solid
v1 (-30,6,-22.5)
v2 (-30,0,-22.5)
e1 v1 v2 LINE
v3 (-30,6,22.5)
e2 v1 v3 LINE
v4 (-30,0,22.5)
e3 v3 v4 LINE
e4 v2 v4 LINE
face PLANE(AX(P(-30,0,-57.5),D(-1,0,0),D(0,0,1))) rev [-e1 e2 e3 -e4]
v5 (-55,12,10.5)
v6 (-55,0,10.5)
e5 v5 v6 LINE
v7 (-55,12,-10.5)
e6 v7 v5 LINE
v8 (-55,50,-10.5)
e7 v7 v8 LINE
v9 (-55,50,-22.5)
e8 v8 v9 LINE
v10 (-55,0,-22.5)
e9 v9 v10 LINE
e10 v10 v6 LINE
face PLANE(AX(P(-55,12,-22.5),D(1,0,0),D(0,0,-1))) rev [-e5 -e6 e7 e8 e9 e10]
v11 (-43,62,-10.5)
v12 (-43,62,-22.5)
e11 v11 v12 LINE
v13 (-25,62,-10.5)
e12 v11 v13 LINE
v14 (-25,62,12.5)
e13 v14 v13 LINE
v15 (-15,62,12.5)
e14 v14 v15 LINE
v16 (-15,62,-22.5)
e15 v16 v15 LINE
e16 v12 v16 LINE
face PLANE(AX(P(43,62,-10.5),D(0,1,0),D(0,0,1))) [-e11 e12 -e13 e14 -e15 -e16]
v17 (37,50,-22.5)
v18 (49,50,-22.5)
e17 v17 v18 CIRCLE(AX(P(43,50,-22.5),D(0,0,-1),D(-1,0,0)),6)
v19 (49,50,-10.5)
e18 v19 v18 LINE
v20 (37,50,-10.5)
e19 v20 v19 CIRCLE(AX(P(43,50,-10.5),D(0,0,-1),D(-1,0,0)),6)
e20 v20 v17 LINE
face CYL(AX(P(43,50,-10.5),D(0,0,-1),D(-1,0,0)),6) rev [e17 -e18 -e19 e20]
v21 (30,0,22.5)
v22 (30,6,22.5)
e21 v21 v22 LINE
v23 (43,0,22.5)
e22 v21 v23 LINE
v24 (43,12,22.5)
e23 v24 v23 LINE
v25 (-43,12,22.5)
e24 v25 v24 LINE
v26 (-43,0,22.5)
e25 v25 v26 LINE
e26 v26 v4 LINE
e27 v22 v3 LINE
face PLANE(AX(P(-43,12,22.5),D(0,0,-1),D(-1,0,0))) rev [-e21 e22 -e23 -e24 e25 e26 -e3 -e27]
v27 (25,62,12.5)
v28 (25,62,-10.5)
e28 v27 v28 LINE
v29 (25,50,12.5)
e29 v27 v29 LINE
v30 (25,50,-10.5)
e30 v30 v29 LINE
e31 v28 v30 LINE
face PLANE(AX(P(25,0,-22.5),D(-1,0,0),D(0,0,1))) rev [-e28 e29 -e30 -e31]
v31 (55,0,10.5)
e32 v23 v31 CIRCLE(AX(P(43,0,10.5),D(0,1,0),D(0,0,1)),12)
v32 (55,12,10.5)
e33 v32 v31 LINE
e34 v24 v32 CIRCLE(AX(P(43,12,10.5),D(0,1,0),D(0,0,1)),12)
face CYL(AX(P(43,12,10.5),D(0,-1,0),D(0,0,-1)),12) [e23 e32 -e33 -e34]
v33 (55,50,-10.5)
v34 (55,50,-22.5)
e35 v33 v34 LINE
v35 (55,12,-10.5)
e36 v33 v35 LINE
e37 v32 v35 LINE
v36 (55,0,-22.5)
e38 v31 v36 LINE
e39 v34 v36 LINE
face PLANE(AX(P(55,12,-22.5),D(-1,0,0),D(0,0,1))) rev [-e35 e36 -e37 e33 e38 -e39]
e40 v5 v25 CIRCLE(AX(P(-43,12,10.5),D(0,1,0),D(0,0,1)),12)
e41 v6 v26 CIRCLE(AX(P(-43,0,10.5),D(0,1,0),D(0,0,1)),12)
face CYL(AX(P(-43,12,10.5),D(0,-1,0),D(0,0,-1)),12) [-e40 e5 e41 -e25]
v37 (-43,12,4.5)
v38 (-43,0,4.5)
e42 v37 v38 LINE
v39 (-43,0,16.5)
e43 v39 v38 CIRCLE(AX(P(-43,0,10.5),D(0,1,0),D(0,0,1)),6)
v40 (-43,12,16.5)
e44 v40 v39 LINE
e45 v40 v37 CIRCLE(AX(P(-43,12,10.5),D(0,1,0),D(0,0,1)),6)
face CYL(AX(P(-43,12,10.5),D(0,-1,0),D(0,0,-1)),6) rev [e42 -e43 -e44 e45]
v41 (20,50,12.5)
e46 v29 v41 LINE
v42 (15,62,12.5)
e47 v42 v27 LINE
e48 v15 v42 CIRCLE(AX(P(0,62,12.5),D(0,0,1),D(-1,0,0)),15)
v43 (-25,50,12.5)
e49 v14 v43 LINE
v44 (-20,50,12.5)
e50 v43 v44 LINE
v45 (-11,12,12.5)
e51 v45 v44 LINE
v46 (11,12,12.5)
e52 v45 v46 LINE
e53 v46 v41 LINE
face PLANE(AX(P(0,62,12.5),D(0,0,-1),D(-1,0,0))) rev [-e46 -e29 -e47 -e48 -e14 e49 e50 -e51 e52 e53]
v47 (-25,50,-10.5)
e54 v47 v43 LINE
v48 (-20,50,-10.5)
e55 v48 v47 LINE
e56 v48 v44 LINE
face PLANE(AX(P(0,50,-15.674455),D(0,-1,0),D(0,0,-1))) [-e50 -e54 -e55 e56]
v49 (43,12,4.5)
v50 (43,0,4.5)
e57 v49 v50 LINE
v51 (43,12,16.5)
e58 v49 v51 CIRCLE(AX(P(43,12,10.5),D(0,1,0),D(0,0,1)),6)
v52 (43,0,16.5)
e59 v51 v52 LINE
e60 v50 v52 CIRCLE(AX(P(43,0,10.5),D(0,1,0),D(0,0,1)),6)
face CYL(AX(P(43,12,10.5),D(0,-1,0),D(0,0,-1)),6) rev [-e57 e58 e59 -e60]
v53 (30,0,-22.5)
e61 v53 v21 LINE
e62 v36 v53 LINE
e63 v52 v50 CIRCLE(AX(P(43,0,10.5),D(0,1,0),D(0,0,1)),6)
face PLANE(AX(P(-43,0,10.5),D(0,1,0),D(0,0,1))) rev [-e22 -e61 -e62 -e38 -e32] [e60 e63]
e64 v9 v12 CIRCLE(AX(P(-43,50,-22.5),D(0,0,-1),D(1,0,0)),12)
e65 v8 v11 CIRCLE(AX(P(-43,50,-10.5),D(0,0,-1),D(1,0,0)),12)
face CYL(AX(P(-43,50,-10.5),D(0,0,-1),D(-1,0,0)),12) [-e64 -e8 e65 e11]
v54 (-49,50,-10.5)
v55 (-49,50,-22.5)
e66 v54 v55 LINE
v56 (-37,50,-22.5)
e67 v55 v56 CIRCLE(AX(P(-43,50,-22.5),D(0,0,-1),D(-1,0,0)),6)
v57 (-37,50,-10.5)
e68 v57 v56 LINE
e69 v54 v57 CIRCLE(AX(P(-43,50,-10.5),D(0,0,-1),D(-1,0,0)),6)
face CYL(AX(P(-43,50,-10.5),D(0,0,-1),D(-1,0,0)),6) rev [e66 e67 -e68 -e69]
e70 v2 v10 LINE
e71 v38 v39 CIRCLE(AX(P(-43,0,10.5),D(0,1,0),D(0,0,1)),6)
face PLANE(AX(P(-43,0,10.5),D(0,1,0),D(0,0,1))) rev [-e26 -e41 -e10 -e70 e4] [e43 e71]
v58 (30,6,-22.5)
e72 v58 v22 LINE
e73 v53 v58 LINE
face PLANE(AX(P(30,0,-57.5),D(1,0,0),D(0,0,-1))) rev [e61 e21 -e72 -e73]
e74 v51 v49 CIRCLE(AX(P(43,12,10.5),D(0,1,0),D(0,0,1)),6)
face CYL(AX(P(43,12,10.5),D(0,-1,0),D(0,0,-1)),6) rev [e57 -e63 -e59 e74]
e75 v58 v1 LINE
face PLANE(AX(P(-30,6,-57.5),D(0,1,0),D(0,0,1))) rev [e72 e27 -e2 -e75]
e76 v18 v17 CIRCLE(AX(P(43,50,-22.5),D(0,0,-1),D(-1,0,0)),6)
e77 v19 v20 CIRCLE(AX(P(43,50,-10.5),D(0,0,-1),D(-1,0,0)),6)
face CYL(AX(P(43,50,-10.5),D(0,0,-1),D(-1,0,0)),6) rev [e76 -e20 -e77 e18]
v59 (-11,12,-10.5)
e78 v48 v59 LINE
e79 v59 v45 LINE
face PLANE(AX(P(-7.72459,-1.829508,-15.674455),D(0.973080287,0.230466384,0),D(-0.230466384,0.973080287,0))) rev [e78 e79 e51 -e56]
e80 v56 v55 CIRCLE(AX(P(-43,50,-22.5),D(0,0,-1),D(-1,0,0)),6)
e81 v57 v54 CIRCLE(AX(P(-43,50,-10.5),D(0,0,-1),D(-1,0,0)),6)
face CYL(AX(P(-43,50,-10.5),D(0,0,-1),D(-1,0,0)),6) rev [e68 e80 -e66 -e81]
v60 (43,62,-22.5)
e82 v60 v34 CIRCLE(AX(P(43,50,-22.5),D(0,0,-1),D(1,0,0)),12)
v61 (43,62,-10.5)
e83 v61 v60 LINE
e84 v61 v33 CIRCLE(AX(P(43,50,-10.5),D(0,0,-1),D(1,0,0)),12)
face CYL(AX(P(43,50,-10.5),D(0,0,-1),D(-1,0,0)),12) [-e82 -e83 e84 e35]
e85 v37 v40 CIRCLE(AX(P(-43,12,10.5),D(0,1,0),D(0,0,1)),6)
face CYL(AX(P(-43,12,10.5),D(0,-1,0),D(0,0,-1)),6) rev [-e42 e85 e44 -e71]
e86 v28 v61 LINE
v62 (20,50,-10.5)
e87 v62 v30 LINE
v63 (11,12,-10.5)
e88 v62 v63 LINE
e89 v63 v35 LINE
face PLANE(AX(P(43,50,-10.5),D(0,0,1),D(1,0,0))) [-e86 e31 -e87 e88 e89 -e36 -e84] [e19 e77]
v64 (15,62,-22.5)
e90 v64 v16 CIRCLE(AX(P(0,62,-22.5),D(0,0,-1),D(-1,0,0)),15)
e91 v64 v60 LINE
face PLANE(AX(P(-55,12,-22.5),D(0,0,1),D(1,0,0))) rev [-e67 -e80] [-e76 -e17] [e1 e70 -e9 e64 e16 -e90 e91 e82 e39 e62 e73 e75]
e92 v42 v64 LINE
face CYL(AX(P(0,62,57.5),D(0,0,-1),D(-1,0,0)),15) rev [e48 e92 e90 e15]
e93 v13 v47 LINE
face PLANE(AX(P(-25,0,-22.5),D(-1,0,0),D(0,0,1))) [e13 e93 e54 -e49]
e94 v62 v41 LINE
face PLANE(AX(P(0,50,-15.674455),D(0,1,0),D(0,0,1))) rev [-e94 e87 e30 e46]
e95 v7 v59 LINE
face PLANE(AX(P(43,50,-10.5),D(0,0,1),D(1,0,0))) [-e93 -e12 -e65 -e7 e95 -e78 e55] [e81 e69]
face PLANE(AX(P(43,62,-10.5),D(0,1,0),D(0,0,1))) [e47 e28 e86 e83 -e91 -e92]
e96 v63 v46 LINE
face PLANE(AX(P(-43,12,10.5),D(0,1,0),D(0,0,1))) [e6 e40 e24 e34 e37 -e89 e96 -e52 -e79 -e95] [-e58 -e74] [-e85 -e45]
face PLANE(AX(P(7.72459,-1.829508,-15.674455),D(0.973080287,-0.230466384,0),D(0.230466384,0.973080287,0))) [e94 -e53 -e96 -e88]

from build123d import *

# Parameters (mm, degrees)
BASE_PLATE_SKETCH_R            = 6
BASE_PLATE_110X45X12_DEPTH     = 12
BACK_WALL_SKETCH_R             = 6
BACK_WALL_12MM_DEPTH           = 12
BASE_UNDERSIDE_SLOT_SKETCH_W   = 60
BASE_UNDERSIDE_SLOT_SKETCH_H   = 6
BASE_UNDERSIDE_SLOT_60X6_DEPTH = 80
TROUGH_BORE_SKETCH_R           = 15
TROUGH_BORE_CUT_DEPTH          = 80
PEDESTAL_BLOCK_DEPTH           = 35
PEDESTAL_START                 = -23
PEDESTAL_SIDE_TRIM_CUT_DEPTH   = 23
PEDESTAL_START_2               = -35
PEDESTAL_WEB_BOSS_DEPTH        = 35


with BuildPart() as part:
    # Base Plate Sketch → Base Plate 110x45x12 (new body)
    with BuildSketch(Plane(origin=(0, 0, 0), x_dir=(1, 0, 0), z_dir=(0, 1, 0))):
        with BuildLine():
            Line((-55, 22.5), (55, 22.5))
            Line((55, 22.5), (55, -10.5))
            ThreePointArc((55, -10.5), (51.485281374, -18.985281374), (43, -22.5))
            Line((43, -22.5), (-43, -22.5))
            ThreePointArc((-43, -22.5), (-51.485281374, -18.985281374), (-55, -10.5))
            Line((-55, -10.5), (-55, 22.5))
        make_face()
        with Locations(Location((-43, -10.5, 0), (0, 0, 270))):
            Circle(BASE_PLATE_SKETCH_R, mode=Mode.SUBTRACT)
        with Locations(Location((43, -10.5, 0), (0, 0, 270))):
            Circle(BASE_PLATE_SKETCH_R, mode=Mode.SUBTRACT)
    extrude(amount=BASE_PLATE_110X45X12_DEPTH)

    # Back Wall Sketch → Back Wall 12mm (add)
    with BuildSketch(Plane(origin=(0, 0, -22.5), x_dir=(-1, 0, 0), z_dir=(0, 0, -1))):
        with BuildLine():
            Line((-55, 0), (55, 0))
            Line((55, 0), (55, 50))
            ThreePointArc((55, 50), (51.485281374, 58.485281374), (43, 62))
            Line((43, 62), (-43, 62))
            ThreePointArc((-43, 62), (-51.485281374, 58.485281374), (-55, 50))
            Line((-55, 50), (-55, 0))
        make_face()
        with Locations((-43, 50)):
            Circle(BACK_WALL_SKETCH_R, mode=Mode.SUBTRACT)
        with Locations((43, 50)):
            Circle(BACK_WALL_SKETCH_R, mode=Mode.SUBTRACT)
    extrude(amount=-BACK_WALL_12MM_DEPTH)

    # Base Underside Slot Sketch → Base Underside Slot 60x6 (cut)
    with BuildSketch(Plane.XY.offset(22.5)):
        with Locations((0, 3)):
            Rectangle(BASE_UNDERSIDE_SLOT_SKETCH_W, BASE_UNDERSIDE_SLOT_SKETCH_H)
    extrude(amount=-BASE_UNDERSIDE_SLOT_60X6_DEPTH, mode=Mode.SUBTRACT)

    # Trough Bore Sketch → Trough Bore Cut (cut)
    with BuildSketch(Plane(origin=(0, 0, -22.5), x_dir=(-1, 0, 0), z_dir=(0, 0, -1))):
        with Locations((0, 62)):
            Circle(TROUGH_BORE_SKETCH_R)
    extrude(amount=-TROUGH_BORE_CUT_DEPTH, mode=Mode.SUBTRACT)

    # Pedestal Block Sketch → Pedestal Block (add)
    with BuildSketch(Plane(origin=(0, 0, -22.5), x_dir=(-1, 0, 0), z_dir=(0, 0, -1))):
        with BuildLine():
            Line((-25, 62), (-15, 62))
            ThreePointArc((-15, 62), (0, 47), (15, 62))
            Line((15, 62), (25, 62))
            ThreePointArc((25, 62), (0, 37), (-25, 62))
        make_face()
    extrude(amount=-PEDESTAL_BLOCK_DEPTH)

    # Pedestal Profile Sketch → Pedestal Side Trim Cut (cut)
    with BuildSketch(Plane.XY.offset(12.5).offset(PEDESTAL_START)):
        with BuildLine():
            ThreePointArc((-21.931712199, 50), (-20.572082469, 47.794739605), (-18.991532718, 45.742027032))
            Line((-18.991532718, 45.742027032), (-20, 50))
            Line((-20, 50), (-21.931712199, 50))
        make_face()
        with BuildLine():
            Line((20, 50), (18.991532718, 45.742027032))
            ThreePointArc((18.991532718, 45.742027032), (20.572082469, 47.794739605), (21.931712199, 50))
            Line((21.931712199, 50), (20, 50))
        make_face()
    extrude(amount=PEDESTAL_SIDE_TRIM_CUT_DEPTH, mode=Mode.SUBTRACT)

    # Sketch6_3 → Pedestal Web Boss (add)
    with BuildSketch(Plane.XY.offset(12.5).offset(PEDESTAL_START_2)):
        with BuildLine():
            Line((-20, 50), (-18.991532718, 45.742027032))
            ThreePointArc((-18.991532718, 45.742027032), (0, 37), (18.991532718, 45.742027032))
            Line((18.991532718, 45.742027032), (20, 50))
            Line((20, 50), (21.931712199, 50))
            ThreePointArc((21.931712199, 50), (24.220784514, 55.806971863), (25, 62))
            Line((25, 62), (15, 62))
            ThreePointArc((15, 62), (0, 47), (-15, 62))
            Line((-15, 62), (-25, 62))
            ThreePointArc((-25, 62), (-24.220784514, 55.806971863), (-21.931712199, 50))
            Line((-21.931712199, 50), (-20, 50))
        make_face()
        with BuildLine():
            Line((-25, 50), (-21.931712199, 50))
            ThreePointArc((-21.931712199, 50), (-24.220784514, 55.806971863), (-25, 62))
            Line((-25, 62), (-25, 50))
        make_face()
        with BuildLine():
            ThreePointArc((25, 62), (24.220784514, 55.806971863), (21.931712199, 50))
            Line((21.931712199, 50), (25, 50))
            Line((25, 50), (25, 62))
        make_face()
        with BuildLine():
            Line((-18.991532718, 45.742027032), (-11, 12))
            Line((-11, 12), (11, 12))
            Line((11, 12), (18.991532718, 45.742027032))
            ThreePointArc((18.991532718, 45.742027032), (0, 37), (-18.991532718, 45.742027032))
        make_face()
    extrude(amount=PEDESTAL_WEB_BOSS_DEPTH)


solid = part.part
